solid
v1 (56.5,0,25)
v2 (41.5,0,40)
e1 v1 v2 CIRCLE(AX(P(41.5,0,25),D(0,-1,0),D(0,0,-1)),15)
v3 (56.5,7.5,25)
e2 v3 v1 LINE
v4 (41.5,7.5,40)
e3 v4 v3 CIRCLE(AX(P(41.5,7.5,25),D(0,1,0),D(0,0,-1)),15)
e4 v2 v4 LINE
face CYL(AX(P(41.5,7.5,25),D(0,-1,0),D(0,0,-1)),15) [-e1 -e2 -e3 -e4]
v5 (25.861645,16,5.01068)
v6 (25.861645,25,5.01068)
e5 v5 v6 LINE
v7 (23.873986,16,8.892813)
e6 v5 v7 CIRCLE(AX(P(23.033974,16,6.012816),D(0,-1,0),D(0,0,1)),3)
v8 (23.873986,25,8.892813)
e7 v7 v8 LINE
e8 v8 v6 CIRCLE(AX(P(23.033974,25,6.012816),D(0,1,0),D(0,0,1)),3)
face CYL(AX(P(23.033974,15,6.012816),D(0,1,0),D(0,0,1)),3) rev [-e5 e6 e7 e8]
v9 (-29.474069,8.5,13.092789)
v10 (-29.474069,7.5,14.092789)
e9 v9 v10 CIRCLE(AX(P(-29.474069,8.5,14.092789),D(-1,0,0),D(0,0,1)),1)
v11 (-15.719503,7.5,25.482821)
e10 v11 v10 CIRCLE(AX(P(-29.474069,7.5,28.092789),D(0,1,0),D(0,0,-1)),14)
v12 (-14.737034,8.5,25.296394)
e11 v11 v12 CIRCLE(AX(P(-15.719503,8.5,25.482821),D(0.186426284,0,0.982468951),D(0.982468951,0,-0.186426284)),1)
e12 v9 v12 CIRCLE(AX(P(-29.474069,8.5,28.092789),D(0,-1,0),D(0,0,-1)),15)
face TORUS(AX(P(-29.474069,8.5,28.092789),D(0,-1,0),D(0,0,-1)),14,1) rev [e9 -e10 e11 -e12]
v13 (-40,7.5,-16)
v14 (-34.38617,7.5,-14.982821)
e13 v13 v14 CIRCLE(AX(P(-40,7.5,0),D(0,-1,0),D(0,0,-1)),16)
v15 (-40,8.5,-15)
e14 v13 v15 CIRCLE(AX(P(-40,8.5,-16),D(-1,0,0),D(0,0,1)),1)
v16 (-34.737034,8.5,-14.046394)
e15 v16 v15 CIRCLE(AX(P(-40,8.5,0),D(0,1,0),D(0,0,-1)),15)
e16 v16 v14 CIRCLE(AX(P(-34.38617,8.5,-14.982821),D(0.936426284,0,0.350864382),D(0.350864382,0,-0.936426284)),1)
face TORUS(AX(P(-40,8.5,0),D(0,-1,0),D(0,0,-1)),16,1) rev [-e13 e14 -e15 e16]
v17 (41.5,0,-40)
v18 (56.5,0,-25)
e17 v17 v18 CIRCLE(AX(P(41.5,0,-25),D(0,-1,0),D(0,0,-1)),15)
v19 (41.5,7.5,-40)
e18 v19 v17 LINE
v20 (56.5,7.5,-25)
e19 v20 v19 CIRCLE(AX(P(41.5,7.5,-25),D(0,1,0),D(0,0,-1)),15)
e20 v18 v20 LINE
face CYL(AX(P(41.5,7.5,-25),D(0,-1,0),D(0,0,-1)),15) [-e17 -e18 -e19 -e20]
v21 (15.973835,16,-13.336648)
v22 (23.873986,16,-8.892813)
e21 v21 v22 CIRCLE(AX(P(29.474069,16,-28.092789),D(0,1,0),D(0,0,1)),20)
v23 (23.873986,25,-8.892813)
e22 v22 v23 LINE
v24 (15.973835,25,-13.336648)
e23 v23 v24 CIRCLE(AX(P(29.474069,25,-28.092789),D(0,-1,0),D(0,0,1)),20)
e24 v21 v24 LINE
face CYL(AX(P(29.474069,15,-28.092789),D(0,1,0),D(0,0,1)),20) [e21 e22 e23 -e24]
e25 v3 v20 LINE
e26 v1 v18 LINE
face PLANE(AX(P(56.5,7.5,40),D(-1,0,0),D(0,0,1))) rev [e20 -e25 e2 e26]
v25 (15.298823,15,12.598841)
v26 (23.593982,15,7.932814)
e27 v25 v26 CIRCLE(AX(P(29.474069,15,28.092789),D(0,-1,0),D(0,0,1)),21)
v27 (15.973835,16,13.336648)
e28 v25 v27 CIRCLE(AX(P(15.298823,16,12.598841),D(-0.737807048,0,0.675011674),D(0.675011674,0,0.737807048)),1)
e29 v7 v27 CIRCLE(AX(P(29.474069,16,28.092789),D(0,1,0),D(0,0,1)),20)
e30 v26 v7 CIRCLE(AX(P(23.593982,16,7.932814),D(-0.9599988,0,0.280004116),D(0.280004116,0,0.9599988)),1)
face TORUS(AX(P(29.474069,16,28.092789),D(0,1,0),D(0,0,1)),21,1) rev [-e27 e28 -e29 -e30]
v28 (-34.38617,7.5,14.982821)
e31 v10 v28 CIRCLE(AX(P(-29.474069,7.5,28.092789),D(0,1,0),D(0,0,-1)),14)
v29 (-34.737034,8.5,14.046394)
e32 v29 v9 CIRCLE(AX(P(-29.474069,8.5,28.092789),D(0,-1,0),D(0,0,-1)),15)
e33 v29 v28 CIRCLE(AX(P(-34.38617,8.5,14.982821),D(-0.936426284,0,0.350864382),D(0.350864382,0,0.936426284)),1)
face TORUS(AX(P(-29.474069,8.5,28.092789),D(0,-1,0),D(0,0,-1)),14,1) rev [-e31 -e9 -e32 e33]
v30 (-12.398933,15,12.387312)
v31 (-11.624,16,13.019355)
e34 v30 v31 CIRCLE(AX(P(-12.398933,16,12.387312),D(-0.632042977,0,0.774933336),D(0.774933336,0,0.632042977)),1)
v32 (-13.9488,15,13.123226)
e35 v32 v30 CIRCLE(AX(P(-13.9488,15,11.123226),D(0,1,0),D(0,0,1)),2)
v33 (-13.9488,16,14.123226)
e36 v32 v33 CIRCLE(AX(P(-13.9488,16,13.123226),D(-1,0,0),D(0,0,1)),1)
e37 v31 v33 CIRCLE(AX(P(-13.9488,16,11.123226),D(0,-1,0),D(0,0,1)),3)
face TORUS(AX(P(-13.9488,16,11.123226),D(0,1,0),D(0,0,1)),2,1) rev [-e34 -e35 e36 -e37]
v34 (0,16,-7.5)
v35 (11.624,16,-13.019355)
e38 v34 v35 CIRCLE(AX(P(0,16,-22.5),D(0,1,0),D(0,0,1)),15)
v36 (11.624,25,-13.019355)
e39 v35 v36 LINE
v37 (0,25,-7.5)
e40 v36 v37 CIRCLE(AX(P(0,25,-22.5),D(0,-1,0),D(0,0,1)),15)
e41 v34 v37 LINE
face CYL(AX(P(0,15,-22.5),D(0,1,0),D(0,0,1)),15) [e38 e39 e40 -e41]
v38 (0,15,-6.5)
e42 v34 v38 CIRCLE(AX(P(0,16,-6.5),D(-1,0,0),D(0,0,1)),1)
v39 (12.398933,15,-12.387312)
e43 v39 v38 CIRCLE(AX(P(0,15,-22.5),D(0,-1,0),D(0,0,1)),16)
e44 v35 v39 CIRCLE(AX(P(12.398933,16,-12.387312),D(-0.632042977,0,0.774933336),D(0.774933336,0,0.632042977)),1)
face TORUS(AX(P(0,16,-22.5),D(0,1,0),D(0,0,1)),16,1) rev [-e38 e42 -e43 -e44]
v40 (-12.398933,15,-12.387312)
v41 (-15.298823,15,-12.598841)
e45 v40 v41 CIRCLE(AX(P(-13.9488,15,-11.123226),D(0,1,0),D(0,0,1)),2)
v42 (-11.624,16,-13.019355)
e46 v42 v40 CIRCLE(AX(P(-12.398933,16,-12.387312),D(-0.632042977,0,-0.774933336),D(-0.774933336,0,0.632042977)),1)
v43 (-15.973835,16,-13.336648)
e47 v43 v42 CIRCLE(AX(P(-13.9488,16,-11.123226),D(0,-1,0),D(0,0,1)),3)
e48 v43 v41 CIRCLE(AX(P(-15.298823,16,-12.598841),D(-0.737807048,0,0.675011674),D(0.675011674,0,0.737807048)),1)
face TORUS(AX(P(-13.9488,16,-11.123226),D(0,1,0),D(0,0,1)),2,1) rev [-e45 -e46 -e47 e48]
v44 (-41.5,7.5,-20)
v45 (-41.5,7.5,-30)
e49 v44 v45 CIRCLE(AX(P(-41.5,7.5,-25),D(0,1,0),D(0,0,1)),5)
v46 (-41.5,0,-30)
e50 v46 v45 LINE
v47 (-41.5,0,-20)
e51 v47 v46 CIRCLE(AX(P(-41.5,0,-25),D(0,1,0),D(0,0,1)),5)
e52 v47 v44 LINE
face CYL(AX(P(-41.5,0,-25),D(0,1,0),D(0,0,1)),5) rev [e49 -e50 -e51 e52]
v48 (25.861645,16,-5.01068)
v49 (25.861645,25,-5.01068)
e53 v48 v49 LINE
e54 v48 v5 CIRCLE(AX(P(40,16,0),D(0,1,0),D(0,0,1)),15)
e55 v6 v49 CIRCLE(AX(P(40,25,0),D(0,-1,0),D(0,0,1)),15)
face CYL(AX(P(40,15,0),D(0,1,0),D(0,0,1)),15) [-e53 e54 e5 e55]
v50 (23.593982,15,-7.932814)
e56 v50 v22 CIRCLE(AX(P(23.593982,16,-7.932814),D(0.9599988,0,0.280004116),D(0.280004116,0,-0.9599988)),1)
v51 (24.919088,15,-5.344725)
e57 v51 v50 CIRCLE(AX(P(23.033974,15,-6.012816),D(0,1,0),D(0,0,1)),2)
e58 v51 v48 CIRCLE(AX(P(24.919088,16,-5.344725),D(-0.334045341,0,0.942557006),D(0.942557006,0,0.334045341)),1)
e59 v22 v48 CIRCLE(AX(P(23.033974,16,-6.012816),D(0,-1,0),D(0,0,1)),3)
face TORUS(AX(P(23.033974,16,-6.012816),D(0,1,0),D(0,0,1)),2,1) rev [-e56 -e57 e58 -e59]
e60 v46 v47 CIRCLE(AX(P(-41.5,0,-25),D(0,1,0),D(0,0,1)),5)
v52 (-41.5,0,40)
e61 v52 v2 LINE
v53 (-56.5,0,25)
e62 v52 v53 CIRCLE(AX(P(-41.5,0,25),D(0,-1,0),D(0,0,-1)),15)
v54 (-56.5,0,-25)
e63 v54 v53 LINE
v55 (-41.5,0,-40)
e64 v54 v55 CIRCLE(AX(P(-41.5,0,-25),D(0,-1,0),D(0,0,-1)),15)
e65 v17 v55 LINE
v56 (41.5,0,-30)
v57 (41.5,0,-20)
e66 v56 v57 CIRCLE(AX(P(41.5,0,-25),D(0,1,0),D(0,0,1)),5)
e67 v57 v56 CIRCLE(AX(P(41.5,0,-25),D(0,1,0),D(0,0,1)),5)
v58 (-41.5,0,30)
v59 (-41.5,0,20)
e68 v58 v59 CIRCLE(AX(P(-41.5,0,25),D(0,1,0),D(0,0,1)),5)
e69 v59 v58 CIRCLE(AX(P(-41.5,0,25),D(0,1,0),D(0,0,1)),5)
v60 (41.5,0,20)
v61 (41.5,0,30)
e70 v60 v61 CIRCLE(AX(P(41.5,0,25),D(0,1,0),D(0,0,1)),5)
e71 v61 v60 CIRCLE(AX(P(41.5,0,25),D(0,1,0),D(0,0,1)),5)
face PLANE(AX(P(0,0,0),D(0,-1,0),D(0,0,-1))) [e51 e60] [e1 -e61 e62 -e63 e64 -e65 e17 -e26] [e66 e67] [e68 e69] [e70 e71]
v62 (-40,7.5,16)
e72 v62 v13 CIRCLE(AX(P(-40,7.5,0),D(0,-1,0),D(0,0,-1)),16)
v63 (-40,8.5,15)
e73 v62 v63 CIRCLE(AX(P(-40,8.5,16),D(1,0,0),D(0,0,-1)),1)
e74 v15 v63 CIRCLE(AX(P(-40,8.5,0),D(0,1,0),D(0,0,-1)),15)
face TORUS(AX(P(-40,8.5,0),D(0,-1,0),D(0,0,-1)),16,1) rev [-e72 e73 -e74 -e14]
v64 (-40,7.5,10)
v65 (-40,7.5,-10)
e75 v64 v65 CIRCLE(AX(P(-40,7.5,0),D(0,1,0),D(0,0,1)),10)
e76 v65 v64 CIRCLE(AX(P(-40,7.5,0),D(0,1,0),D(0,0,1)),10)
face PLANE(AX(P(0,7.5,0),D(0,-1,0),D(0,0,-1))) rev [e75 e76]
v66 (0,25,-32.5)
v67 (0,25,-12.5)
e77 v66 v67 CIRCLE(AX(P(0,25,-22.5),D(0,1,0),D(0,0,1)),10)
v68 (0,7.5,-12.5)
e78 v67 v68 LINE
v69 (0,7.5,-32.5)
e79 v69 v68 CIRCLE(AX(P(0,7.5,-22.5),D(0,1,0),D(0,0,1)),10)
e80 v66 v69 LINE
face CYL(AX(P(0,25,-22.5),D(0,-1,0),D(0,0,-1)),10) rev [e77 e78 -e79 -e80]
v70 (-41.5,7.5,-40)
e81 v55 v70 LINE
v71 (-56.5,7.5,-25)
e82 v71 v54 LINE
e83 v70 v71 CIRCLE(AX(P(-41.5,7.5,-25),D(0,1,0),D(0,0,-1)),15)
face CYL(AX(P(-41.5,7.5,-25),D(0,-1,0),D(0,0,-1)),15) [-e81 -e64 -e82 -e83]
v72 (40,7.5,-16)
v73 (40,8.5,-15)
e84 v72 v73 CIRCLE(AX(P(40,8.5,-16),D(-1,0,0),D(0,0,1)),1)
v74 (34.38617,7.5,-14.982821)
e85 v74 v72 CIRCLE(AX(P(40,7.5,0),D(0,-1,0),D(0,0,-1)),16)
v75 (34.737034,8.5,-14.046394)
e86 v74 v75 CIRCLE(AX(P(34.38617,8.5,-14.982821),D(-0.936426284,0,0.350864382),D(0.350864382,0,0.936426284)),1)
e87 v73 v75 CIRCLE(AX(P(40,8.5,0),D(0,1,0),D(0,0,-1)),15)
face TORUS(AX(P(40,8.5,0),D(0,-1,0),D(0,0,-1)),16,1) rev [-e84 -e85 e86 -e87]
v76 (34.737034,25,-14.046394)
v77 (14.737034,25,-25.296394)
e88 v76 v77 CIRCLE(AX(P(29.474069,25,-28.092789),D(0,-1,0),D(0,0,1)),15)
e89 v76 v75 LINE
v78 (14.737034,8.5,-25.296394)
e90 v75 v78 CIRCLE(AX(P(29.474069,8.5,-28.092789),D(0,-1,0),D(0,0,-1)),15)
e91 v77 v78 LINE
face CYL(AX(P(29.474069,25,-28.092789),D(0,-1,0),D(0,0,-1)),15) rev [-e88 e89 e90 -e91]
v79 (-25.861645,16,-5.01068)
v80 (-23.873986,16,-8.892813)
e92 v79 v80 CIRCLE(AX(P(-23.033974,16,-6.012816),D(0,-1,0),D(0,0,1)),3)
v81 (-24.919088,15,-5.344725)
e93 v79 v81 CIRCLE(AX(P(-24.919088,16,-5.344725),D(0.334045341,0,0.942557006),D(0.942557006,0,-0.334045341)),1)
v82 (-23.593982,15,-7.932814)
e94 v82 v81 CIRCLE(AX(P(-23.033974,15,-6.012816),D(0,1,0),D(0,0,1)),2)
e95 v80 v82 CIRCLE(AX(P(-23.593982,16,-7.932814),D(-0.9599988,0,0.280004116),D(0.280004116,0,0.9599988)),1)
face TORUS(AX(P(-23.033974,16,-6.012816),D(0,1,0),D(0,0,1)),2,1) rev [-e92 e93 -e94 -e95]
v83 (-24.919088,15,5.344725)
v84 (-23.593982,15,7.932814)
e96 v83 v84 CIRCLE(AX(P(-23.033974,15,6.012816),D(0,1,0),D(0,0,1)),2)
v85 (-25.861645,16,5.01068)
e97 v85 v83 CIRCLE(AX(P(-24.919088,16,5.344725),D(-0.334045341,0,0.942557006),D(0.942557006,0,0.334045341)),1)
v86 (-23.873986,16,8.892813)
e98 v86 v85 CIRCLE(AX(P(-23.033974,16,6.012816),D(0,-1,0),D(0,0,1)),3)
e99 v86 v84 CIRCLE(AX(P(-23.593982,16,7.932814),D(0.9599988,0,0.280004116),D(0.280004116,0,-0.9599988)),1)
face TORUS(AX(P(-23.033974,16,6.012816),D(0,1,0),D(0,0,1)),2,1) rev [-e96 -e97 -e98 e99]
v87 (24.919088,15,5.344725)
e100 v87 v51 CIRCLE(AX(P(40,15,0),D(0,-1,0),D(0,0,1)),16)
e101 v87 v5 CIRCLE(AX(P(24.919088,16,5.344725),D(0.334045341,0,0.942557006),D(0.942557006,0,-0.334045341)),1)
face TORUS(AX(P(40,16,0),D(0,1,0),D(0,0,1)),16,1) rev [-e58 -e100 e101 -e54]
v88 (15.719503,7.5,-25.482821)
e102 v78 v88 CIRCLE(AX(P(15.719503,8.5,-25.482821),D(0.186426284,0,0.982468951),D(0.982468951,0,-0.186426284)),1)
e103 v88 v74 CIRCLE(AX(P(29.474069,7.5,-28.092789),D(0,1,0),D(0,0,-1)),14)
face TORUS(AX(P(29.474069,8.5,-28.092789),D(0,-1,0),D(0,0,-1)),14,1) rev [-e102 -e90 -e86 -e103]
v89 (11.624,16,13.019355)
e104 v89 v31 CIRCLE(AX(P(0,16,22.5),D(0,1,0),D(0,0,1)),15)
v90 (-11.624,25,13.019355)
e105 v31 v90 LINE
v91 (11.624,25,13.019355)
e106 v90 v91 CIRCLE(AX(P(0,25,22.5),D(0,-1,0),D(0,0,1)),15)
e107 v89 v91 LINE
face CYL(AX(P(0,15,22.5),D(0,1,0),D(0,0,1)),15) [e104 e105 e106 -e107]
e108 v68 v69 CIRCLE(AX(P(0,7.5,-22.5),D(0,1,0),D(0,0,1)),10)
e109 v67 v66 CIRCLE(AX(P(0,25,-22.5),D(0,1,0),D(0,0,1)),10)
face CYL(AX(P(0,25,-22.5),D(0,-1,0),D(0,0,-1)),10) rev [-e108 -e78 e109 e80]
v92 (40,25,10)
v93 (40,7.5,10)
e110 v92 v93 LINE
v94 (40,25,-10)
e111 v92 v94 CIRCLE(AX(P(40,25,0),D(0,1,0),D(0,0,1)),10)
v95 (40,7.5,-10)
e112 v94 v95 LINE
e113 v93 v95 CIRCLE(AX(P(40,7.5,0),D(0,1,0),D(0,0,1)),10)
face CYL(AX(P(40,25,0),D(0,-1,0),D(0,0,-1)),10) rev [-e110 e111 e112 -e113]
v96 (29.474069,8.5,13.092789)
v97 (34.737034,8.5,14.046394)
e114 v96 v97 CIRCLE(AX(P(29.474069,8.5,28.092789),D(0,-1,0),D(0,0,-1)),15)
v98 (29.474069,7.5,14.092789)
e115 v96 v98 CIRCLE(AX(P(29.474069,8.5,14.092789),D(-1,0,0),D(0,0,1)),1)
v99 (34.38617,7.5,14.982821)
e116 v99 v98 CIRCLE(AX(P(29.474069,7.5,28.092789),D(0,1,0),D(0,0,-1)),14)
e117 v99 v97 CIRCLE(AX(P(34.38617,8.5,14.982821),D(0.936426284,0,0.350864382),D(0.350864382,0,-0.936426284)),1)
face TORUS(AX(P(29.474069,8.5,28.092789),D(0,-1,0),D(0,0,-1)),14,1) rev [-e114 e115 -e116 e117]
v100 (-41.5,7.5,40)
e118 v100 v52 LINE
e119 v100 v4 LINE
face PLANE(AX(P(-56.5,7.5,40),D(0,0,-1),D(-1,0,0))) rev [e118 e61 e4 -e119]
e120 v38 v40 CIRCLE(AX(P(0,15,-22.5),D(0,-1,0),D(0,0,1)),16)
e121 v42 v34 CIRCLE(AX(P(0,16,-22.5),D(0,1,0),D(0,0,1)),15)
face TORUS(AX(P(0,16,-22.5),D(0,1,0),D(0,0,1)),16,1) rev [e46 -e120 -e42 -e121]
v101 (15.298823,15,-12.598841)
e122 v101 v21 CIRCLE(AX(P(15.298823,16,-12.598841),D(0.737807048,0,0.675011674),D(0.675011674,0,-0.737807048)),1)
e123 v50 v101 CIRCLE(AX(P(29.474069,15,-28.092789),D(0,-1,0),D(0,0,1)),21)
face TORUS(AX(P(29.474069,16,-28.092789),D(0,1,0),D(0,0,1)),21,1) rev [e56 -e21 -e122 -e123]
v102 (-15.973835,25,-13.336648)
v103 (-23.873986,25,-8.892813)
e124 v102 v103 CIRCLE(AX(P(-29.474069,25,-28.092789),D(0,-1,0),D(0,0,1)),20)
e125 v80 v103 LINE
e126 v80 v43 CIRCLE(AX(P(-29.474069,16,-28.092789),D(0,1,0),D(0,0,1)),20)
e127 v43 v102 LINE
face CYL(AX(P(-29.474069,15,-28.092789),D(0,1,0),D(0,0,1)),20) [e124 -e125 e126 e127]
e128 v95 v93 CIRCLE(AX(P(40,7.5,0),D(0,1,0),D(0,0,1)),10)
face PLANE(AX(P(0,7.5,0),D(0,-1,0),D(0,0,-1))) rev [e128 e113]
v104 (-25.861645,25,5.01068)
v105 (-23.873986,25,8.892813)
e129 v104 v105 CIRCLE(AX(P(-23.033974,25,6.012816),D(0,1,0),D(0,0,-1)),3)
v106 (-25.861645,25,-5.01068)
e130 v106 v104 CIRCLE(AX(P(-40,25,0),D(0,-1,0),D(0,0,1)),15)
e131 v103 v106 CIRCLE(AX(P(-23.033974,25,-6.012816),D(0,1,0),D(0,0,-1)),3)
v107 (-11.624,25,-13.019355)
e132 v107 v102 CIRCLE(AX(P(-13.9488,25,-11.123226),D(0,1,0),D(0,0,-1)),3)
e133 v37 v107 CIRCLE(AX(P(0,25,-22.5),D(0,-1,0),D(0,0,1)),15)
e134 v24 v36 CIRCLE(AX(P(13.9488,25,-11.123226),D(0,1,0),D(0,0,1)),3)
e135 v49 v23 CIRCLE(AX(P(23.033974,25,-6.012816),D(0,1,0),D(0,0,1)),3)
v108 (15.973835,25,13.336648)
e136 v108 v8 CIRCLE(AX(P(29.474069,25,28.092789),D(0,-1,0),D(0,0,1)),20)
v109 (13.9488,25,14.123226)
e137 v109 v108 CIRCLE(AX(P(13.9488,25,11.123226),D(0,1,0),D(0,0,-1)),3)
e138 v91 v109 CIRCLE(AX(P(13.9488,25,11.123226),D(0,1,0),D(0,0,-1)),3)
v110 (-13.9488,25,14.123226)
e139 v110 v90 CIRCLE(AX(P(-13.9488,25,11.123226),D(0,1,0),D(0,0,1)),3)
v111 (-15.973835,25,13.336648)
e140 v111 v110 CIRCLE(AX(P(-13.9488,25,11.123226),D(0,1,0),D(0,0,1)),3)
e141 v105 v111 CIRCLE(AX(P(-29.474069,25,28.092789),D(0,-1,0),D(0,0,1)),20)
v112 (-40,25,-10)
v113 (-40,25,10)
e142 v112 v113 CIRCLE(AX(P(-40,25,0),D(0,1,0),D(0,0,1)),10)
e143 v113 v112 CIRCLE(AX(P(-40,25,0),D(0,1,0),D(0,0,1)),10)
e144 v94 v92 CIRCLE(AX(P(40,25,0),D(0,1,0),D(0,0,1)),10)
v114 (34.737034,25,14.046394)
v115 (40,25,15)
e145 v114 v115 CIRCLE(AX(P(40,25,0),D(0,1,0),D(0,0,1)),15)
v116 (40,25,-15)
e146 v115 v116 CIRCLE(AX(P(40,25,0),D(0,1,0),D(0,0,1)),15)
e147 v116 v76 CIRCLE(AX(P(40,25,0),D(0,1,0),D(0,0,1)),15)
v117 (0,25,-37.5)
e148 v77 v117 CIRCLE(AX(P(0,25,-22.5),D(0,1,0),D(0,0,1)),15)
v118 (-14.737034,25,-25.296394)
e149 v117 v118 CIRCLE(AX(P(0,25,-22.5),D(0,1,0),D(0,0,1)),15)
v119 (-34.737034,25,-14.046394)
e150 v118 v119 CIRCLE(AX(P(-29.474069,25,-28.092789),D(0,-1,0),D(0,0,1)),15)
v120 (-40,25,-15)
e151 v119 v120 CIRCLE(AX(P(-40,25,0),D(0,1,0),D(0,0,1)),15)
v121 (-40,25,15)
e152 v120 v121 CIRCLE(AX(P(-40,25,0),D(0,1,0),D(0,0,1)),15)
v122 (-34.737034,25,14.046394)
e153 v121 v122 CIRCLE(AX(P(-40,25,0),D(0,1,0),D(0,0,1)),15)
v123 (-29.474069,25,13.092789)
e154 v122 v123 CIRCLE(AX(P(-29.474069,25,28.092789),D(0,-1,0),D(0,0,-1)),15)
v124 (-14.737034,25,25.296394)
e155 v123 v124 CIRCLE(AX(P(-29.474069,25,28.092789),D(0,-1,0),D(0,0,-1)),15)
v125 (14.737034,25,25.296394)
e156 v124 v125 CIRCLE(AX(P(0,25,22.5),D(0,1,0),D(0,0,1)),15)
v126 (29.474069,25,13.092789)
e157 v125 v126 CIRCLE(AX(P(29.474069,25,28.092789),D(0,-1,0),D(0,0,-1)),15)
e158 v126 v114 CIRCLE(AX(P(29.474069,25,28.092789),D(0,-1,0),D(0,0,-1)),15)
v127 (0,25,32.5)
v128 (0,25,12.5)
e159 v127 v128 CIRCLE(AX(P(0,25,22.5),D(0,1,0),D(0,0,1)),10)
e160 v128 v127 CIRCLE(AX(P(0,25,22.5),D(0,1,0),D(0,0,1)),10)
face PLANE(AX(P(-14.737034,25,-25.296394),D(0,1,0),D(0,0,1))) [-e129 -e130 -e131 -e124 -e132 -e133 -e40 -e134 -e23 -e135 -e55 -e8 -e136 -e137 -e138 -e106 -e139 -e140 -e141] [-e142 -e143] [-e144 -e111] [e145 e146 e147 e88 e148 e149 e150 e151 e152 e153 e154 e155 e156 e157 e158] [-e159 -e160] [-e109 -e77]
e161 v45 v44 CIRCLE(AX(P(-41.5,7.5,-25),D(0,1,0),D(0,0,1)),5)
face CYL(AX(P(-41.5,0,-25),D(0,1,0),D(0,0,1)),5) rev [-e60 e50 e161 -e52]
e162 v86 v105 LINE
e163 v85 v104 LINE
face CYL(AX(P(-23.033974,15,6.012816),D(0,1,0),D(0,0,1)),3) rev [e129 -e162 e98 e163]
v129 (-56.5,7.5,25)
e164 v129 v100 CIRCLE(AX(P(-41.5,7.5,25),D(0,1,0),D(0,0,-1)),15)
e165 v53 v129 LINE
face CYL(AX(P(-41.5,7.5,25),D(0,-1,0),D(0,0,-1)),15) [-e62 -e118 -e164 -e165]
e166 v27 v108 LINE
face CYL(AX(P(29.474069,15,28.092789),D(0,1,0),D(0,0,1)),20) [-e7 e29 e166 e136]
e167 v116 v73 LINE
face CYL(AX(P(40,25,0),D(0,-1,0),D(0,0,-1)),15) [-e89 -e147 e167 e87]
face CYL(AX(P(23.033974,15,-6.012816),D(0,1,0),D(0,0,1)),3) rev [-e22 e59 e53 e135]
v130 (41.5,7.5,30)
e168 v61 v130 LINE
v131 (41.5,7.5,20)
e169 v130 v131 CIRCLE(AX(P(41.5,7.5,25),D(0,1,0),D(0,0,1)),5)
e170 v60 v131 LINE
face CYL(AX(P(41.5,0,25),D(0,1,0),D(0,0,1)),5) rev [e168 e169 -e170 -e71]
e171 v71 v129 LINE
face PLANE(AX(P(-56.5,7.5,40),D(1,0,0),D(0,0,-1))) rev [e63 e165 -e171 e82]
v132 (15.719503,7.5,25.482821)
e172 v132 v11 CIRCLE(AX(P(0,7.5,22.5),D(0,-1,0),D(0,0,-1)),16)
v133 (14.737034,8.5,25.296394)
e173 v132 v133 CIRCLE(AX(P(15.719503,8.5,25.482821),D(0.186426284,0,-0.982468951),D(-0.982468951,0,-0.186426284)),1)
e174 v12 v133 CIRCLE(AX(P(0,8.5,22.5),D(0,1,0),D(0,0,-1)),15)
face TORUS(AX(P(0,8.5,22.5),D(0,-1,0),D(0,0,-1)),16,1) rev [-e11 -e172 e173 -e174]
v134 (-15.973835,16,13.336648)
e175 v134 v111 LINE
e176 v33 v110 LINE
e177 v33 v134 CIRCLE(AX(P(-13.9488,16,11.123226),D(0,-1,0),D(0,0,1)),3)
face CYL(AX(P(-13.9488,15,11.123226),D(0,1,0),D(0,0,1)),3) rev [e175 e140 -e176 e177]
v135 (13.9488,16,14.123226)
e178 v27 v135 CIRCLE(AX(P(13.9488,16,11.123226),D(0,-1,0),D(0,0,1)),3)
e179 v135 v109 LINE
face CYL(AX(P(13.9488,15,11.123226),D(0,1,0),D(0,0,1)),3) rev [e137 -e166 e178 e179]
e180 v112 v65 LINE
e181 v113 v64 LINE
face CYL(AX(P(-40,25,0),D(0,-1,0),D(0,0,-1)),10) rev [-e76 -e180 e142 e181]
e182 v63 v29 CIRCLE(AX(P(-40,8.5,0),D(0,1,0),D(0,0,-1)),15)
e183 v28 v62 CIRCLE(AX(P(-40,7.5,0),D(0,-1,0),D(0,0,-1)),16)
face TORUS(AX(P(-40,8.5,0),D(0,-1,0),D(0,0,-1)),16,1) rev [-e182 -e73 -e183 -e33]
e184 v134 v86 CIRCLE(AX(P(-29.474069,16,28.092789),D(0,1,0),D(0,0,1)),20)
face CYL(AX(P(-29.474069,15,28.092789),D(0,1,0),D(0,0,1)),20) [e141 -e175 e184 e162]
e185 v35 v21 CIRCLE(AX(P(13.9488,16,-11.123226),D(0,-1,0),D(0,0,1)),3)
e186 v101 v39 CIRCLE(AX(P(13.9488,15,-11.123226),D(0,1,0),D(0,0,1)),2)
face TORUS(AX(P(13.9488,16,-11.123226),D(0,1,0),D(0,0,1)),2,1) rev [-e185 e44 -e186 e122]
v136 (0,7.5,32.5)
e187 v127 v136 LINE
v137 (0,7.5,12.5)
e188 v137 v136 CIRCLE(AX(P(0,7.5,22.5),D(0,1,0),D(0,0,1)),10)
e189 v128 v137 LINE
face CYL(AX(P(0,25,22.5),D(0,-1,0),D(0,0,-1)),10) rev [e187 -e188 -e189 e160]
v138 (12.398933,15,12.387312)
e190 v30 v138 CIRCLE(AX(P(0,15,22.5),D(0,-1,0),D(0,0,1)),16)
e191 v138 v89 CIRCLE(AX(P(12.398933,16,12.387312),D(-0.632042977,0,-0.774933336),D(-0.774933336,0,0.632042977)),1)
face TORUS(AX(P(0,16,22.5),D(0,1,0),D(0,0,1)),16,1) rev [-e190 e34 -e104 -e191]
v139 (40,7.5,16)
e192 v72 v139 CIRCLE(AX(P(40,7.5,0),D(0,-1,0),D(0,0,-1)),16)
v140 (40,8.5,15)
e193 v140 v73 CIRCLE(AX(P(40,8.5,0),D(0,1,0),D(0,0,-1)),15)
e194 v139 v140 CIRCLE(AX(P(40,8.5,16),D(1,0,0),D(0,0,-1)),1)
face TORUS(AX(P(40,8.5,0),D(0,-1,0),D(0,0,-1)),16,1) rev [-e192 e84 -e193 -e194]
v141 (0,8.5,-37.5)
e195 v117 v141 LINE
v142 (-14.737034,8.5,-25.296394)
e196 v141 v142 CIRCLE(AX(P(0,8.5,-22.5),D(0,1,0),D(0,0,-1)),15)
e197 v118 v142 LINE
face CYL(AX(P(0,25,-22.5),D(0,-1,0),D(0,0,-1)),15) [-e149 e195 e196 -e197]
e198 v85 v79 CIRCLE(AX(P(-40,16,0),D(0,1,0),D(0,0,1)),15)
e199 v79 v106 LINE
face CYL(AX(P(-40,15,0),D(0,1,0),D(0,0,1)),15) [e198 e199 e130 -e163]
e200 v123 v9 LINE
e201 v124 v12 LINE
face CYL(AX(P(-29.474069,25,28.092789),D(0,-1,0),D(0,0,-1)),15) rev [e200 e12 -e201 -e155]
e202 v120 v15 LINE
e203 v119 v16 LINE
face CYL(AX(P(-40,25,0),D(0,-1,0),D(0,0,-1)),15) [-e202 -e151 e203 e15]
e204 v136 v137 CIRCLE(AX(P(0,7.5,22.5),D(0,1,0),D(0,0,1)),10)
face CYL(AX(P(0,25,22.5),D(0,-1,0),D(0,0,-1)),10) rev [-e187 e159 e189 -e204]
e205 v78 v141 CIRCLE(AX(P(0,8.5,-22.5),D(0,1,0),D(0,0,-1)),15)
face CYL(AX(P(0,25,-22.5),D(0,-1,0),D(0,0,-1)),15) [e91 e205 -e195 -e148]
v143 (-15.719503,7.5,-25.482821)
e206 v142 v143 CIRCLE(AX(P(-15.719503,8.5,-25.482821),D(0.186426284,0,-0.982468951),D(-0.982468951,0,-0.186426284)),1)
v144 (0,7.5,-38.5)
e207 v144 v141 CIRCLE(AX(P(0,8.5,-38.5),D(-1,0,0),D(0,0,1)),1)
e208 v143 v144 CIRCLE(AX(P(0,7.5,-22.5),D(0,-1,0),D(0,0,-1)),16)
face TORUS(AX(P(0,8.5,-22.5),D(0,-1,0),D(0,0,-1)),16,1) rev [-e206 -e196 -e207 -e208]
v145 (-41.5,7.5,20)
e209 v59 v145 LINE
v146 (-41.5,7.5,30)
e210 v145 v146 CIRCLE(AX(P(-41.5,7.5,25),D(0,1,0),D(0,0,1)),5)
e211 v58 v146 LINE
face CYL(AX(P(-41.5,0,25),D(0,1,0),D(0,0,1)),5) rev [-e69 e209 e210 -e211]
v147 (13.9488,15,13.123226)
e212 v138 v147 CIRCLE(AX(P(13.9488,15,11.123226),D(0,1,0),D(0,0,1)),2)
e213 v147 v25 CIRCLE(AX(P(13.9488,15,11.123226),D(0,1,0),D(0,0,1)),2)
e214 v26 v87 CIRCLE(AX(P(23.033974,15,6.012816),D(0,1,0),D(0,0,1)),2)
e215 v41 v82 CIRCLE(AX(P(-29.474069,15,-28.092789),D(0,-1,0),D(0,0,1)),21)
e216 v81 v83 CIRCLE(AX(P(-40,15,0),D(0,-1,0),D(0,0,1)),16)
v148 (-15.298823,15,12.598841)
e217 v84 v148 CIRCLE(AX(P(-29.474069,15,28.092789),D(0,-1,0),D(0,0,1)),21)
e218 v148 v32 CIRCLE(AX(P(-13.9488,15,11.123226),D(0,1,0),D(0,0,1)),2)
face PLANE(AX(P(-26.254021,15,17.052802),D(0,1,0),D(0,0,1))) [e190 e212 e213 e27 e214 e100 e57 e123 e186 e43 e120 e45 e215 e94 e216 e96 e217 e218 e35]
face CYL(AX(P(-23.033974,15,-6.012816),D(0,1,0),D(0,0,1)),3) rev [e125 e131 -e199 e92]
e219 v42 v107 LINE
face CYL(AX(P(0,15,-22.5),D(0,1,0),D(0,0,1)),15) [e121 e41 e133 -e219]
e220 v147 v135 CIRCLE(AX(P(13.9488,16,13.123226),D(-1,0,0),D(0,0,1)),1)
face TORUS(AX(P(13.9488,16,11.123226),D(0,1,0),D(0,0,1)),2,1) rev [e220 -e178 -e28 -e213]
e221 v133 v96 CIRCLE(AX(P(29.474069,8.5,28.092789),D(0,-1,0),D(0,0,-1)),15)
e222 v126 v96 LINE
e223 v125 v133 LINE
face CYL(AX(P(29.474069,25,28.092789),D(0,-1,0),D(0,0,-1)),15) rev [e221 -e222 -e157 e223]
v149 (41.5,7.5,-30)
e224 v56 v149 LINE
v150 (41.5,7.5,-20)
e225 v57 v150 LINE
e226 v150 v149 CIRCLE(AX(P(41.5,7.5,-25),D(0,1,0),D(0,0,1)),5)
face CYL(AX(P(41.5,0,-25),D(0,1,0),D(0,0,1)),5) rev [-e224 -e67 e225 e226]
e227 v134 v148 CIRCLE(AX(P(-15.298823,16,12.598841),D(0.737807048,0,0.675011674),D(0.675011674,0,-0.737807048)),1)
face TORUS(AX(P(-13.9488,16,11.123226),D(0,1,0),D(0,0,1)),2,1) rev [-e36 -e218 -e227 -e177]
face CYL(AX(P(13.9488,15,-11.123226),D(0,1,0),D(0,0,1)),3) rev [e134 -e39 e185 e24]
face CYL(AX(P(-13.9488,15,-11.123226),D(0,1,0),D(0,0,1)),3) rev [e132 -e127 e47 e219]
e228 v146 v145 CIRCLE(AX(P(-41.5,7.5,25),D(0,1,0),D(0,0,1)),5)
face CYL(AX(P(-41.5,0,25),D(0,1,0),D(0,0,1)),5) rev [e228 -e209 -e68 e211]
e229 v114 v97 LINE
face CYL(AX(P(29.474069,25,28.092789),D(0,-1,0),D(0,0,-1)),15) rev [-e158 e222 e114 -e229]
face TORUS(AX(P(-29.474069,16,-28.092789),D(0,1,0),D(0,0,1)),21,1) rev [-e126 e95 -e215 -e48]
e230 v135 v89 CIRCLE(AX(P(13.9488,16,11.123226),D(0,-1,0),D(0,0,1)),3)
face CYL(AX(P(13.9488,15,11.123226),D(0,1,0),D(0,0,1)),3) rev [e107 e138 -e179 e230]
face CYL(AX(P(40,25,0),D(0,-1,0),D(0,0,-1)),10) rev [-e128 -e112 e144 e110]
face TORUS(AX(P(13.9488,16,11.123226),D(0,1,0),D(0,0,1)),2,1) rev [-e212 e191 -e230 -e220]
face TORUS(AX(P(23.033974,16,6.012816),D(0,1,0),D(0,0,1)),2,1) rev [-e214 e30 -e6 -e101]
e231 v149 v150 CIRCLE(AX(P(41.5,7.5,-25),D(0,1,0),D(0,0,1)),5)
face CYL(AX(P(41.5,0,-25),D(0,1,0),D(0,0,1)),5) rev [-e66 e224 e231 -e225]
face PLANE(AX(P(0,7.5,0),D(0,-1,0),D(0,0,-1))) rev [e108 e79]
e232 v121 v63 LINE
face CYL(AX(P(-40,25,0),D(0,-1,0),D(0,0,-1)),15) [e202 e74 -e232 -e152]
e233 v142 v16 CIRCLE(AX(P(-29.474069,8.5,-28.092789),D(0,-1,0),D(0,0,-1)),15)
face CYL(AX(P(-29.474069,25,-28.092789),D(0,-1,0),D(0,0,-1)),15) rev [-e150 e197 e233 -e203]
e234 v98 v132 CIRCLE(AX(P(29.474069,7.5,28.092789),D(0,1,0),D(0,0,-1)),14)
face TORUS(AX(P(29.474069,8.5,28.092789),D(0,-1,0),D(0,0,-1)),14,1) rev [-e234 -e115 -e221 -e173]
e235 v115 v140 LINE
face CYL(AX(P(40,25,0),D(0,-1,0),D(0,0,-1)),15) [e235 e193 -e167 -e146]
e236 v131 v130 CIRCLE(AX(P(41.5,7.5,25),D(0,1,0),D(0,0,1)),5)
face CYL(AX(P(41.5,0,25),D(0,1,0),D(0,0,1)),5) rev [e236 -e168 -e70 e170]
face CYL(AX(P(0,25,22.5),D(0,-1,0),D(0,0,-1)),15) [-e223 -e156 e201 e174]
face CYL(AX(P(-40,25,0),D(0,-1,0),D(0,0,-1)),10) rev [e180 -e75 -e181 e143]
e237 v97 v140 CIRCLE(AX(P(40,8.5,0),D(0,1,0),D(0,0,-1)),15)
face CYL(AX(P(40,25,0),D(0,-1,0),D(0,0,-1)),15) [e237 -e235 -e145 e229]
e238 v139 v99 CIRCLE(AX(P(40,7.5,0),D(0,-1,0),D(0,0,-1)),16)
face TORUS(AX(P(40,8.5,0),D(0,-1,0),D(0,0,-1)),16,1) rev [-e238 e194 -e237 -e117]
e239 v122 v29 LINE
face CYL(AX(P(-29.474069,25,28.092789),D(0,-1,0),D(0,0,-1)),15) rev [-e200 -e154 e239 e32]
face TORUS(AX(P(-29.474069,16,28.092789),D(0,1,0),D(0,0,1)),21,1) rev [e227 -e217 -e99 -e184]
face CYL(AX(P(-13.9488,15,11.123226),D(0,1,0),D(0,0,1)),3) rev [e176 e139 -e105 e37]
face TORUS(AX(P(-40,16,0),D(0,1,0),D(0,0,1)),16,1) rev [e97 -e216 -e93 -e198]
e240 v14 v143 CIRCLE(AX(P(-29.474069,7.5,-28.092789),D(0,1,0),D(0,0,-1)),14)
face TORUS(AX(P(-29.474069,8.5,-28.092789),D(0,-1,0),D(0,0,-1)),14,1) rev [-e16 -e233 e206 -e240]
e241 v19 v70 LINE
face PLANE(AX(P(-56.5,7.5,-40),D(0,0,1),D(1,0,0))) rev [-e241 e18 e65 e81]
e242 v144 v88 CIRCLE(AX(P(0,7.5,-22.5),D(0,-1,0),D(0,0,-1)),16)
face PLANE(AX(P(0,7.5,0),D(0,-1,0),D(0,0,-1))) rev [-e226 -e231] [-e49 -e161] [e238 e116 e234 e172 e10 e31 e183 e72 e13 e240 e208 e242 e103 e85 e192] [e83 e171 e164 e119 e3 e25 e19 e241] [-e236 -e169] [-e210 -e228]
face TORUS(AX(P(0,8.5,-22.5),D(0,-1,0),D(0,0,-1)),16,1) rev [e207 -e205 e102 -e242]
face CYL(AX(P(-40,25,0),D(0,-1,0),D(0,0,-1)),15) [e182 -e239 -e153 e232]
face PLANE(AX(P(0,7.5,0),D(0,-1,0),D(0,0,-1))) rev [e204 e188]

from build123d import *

# Parameters (mm, degrees)
BASE_PLATE_SKETCH_W              = 113
BASE_PLATE_SKETCH_H              = 80
BASE_PLATE_113X80X7_5_DEPTH      = 7.5
PLATE_CORNER_FILLETS_R15_R       = 15
MOUNTING_HOLES_SKETCH_R          = 5
CORNER_MOUNTING_HOLES_4X_DEPTH   = 7.5
BORE_BOSS_CLUSTER_SKETCH_R       = 10
BORE_BOSS_CLUSTER_DEPTH          = 17.5
BORES_START                      = -10
BORES_AND_RELIEF_POCKET_DEPTH    = 10
BOSS_ROOT_FILLET_R1_R            = 1
BORE_AND_POCKET_EDGE_FILLET_R1_R = 1


with BuildPart() as part:
    # Base Plate Sketch → Base Plate 113x80x7.5 (new body)
    with BuildSketch(Plane(origin=(0, 0, 0), x_dir=(1, 0, 0), z_dir=(0, 1, 0))):
        Rectangle(BASE_PLATE_SKETCH_W, BASE_PLATE_SKETCH_H)
    extrude(amount=BASE_PLATE_113X80X7_5_DEPTH)

    # Plate Corner Fillets R15
    plate_corner_fillets_r15_edges = [part.edges().sort_by_distance(p)[0] for p in [
        (56.5, 3.75, 40),
        (-56.5, 3.75, 40),
        (-56.5, 3.75, -40),
        (56.5, 3.75, -40),
    ]]
    fillet(plate_corner_fillets_r15_edges, radius=PLATE_CORNER_FILLETS_R15_R)

    # Mounting Holes Sketch → Corner Mounting Holes 4x (cut)
    with BuildSketch(Plane(origin=(0, 7.5, 0), x_dir=(1, 0, 0), z_dir=(0, 1, 0))):
        with Locations(Location((-41.5, 25, 0), (0, 0, 270))):
            Circle(MOUNTING_HOLES_SKETCH_R)
        with Locations(Location((41.5, 25, 0), (0, 0, 270))):
            Circle(MOUNTING_HOLES_SKETCH_R)
        with Locations(Location((-41.5, -25, 0), (0, 0, 270))):
            Circle(MOUNTING_HOLES_SKETCH_R)
        with Locations(Location((41.5, -25, 0), (0, 0, 270))):
            Circle(MOUNTING_HOLES_SKETCH_R)
    extrude(amount=-CORNER_MOUNTING_HOLES_4X_DEPTH, mode=Mode.SUBTRACT)

    # Bore Boss Cluster Sketch → Bore Boss Cluster (add)
    with BuildSketch(Plane(origin=(0, 7.5, 0), x_dir=(1, 0, 0), z_dir=(0, 1, 0))):
        with BuildLine():
            ThreePointArc((-34.737034272, 14.046394261), (-55, 0), (-34.737034272, -14.046394261))
            ThreePointArc((-34.737034272, -14.046394261), (-22.12014995, -15.019155466), (-14.737034272, -25.296394261))
            ThreePointArc((-14.737034272, -25.296394261), (0, -37.5), (14.737034272, -25.296394261))
            ThreePointArc((14.737034272, -25.296394261), (22.12014995, -15.019155466), (34.737034272, -14.046394261))
            ThreePointArc((34.737034272, -14.046394261), (55, 0), (34.737034272, 14.046394261))
            ThreePointArc((34.737034272, 14.046394261), (22.12014995, 15.019155466), (14.737034272, 25.296394261))
            ThreePointArc((14.737034272, 25.296394261), (0, 37.5), (-14.737034272, 25.296394261))
            ThreePointArc((-14.737034272, 25.296394261), (-22.12014995, 15.019155466), (-34.737034272, 14.046394261))
        make_face()
        with Locations(Location((-40, 0, 0), (0, 0, 270))):
            Circle(BORE_BOSS_CLUSTER_SKETCH_R, mode=Mode.SUBTRACT)
        with Locations(Location((0, 22.5, 0), (0, 0, 270))):
            Circle(BORE_BOSS_CLUSTER_SKETCH_R, mode=Mode.SUBTRACT)
        with Locations(Location((40, 0, 0), (0, 0, 270))):
            Circle(BORE_BOSS_CLUSTER_SKETCH_R, mode=Mode.SUBTRACT)
        with Locations(Location((0, -22.5, 0), (0, 0, 270))):
            Circle(BORE_BOSS_CLUSTER_SKETCH_R, mode=Mode.SUBTRACT)
    extrude(amount=BORE_BOSS_CLUSTER_DEPTH)

    # Bores and Relief Pocket Sketch → Bores and Relief Pocket (cut)
    with BuildSketch(Plane(origin=(0, 25, 0), x_dir=(1, 0, 0), z_dir=(0, 1, 0)).offset(BORES_START)):
        with BuildLine():
            ThreePointArc((-23.873986231, -8.892812531), (-25.704313442, -7.380034713), (-25.861644904, -5.01068011))
            ThreePointArc((-25.861644904, -5.01068011), (-25, 0), (-25.861644904, 5.01068011))
            ThreePointArc((-25.861644904, 5.01068011), (-25.704313442, 7.380034713), (-23.873986231, 8.892812531))
            ThreePointArc((-23.873986231, 8.892812531), (-19.668843751, 10.66127778), (-15.97383507, 13.336647559))
            ThreePointArc((-15.97383507, 13.336647559), (-13.730549392, 14.115276991), (-11.62400004, 13.019355346))
            ThreePointArc((-11.62400004, 13.019355346), (0, 7.5), (11.62400004, 13.019355346))
            ThreePointArc((11.62400004, 13.019355346), (13.730549392, 14.115276991), (15.97383507, 13.336647559))
            ThreePointArc((15.97383507, 13.336647559), (19.668843751, 10.66127778), (23.873986231, 8.892812531))
            ThreePointArc((23.873986231, 8.892812531), (25.704313442, 7.380034713), (25.861644904, 5.01068011))
            ThreePointArc((25.861644904, 5.01068011), (25, 0), (25.861644904, -5.01068011))
            ThreePointArc((25.861644904, -5.01068011), (25.704313442, -7.380034713), (23.873986231, -8.892812531))
            ThreePointArc((23.873986231, -8.892812531), (19.668843751, -10.66127778), (15.97383507, -13.336647559))
            ThreePointArc((15.97383507, -13.336647559), (13.730549392, -14.115276991), (11.62400004, -13.019355346))
            ThreePointArc((11.62400004, -13.019355346), (0, -7.5), (-11.62400004, -13.019355346))
            ThreePointArc((-11.62400004, -13.019355346), (-13.730549392, -14.115276991), (-15.97383507, -13.336647559))
            ThreePointArc((-15.97383507, -13.336647559), (-19.668843751, -10.66127778), (-23.873986231, -8.892812531))
        make_face()
    extrude(amount=BORES_AND_RELIEF_POCKET_DEPTH, mode=Mode.SUBTRACT)

    # Boss Root Fillet R1
    boss_root_fillet_r1_edges = [part.edges().sort_by_distance(p)[0] for p in [
        (-22.12014995, 7.5, -15.019155466),
        (-55, 7.5, 0),
        (-22.12014995, 7.5, 15.019155466),
        (0, 7.5, 37.5),
        (22.12014995, 7.5, 15.019155466),
        (55, 7.5, 0),
        (22.12014995, 7.5, -15.019155466),
        (0, 7.5, -37.5),
    ]]
    fillet(boss_root_fillet_r1_edges, radius=BOSS_ROOT_FILLET_R1_R)

    # Bore and Pocket Edge Fillet R1
    bore_and_pocket_edge_fillet_r1_edges = [part.edges().sort_by_distance(p)[0] for p in [
        (-19.668843751, 15, 10.66127778),
        (-25.704313442, 15, 7.380034713),
        (-25, 15, 0),
        (-25.704313442, 15, -7.380034713),
        (-19.668843751, 15, -10.66127778),
        (-13.730549392, 15, -14.115276991),
        (0, 15, -7.5),
        (13.730549392, 15, -14.115276991),
        (19.668843751, 15, -10.66127778),
        (25.704313442, 15, -7.380034713),
        (25, 15, 0),
        (25.704313442, 15, 7.380034713),
        (19.668843751, 15, 10.66127778),
        (13.730549392, 15, 14.115276991),
        (0, 15, 7.5),
        (-13.730549392, 15, 14.115276991),
    ]]
    fillet(bore_and_pocket_edge_fillet_r1_edges, radius=BORE_AND_POCKET_EDGE_FILLET_R1_R)


solid = part.part
